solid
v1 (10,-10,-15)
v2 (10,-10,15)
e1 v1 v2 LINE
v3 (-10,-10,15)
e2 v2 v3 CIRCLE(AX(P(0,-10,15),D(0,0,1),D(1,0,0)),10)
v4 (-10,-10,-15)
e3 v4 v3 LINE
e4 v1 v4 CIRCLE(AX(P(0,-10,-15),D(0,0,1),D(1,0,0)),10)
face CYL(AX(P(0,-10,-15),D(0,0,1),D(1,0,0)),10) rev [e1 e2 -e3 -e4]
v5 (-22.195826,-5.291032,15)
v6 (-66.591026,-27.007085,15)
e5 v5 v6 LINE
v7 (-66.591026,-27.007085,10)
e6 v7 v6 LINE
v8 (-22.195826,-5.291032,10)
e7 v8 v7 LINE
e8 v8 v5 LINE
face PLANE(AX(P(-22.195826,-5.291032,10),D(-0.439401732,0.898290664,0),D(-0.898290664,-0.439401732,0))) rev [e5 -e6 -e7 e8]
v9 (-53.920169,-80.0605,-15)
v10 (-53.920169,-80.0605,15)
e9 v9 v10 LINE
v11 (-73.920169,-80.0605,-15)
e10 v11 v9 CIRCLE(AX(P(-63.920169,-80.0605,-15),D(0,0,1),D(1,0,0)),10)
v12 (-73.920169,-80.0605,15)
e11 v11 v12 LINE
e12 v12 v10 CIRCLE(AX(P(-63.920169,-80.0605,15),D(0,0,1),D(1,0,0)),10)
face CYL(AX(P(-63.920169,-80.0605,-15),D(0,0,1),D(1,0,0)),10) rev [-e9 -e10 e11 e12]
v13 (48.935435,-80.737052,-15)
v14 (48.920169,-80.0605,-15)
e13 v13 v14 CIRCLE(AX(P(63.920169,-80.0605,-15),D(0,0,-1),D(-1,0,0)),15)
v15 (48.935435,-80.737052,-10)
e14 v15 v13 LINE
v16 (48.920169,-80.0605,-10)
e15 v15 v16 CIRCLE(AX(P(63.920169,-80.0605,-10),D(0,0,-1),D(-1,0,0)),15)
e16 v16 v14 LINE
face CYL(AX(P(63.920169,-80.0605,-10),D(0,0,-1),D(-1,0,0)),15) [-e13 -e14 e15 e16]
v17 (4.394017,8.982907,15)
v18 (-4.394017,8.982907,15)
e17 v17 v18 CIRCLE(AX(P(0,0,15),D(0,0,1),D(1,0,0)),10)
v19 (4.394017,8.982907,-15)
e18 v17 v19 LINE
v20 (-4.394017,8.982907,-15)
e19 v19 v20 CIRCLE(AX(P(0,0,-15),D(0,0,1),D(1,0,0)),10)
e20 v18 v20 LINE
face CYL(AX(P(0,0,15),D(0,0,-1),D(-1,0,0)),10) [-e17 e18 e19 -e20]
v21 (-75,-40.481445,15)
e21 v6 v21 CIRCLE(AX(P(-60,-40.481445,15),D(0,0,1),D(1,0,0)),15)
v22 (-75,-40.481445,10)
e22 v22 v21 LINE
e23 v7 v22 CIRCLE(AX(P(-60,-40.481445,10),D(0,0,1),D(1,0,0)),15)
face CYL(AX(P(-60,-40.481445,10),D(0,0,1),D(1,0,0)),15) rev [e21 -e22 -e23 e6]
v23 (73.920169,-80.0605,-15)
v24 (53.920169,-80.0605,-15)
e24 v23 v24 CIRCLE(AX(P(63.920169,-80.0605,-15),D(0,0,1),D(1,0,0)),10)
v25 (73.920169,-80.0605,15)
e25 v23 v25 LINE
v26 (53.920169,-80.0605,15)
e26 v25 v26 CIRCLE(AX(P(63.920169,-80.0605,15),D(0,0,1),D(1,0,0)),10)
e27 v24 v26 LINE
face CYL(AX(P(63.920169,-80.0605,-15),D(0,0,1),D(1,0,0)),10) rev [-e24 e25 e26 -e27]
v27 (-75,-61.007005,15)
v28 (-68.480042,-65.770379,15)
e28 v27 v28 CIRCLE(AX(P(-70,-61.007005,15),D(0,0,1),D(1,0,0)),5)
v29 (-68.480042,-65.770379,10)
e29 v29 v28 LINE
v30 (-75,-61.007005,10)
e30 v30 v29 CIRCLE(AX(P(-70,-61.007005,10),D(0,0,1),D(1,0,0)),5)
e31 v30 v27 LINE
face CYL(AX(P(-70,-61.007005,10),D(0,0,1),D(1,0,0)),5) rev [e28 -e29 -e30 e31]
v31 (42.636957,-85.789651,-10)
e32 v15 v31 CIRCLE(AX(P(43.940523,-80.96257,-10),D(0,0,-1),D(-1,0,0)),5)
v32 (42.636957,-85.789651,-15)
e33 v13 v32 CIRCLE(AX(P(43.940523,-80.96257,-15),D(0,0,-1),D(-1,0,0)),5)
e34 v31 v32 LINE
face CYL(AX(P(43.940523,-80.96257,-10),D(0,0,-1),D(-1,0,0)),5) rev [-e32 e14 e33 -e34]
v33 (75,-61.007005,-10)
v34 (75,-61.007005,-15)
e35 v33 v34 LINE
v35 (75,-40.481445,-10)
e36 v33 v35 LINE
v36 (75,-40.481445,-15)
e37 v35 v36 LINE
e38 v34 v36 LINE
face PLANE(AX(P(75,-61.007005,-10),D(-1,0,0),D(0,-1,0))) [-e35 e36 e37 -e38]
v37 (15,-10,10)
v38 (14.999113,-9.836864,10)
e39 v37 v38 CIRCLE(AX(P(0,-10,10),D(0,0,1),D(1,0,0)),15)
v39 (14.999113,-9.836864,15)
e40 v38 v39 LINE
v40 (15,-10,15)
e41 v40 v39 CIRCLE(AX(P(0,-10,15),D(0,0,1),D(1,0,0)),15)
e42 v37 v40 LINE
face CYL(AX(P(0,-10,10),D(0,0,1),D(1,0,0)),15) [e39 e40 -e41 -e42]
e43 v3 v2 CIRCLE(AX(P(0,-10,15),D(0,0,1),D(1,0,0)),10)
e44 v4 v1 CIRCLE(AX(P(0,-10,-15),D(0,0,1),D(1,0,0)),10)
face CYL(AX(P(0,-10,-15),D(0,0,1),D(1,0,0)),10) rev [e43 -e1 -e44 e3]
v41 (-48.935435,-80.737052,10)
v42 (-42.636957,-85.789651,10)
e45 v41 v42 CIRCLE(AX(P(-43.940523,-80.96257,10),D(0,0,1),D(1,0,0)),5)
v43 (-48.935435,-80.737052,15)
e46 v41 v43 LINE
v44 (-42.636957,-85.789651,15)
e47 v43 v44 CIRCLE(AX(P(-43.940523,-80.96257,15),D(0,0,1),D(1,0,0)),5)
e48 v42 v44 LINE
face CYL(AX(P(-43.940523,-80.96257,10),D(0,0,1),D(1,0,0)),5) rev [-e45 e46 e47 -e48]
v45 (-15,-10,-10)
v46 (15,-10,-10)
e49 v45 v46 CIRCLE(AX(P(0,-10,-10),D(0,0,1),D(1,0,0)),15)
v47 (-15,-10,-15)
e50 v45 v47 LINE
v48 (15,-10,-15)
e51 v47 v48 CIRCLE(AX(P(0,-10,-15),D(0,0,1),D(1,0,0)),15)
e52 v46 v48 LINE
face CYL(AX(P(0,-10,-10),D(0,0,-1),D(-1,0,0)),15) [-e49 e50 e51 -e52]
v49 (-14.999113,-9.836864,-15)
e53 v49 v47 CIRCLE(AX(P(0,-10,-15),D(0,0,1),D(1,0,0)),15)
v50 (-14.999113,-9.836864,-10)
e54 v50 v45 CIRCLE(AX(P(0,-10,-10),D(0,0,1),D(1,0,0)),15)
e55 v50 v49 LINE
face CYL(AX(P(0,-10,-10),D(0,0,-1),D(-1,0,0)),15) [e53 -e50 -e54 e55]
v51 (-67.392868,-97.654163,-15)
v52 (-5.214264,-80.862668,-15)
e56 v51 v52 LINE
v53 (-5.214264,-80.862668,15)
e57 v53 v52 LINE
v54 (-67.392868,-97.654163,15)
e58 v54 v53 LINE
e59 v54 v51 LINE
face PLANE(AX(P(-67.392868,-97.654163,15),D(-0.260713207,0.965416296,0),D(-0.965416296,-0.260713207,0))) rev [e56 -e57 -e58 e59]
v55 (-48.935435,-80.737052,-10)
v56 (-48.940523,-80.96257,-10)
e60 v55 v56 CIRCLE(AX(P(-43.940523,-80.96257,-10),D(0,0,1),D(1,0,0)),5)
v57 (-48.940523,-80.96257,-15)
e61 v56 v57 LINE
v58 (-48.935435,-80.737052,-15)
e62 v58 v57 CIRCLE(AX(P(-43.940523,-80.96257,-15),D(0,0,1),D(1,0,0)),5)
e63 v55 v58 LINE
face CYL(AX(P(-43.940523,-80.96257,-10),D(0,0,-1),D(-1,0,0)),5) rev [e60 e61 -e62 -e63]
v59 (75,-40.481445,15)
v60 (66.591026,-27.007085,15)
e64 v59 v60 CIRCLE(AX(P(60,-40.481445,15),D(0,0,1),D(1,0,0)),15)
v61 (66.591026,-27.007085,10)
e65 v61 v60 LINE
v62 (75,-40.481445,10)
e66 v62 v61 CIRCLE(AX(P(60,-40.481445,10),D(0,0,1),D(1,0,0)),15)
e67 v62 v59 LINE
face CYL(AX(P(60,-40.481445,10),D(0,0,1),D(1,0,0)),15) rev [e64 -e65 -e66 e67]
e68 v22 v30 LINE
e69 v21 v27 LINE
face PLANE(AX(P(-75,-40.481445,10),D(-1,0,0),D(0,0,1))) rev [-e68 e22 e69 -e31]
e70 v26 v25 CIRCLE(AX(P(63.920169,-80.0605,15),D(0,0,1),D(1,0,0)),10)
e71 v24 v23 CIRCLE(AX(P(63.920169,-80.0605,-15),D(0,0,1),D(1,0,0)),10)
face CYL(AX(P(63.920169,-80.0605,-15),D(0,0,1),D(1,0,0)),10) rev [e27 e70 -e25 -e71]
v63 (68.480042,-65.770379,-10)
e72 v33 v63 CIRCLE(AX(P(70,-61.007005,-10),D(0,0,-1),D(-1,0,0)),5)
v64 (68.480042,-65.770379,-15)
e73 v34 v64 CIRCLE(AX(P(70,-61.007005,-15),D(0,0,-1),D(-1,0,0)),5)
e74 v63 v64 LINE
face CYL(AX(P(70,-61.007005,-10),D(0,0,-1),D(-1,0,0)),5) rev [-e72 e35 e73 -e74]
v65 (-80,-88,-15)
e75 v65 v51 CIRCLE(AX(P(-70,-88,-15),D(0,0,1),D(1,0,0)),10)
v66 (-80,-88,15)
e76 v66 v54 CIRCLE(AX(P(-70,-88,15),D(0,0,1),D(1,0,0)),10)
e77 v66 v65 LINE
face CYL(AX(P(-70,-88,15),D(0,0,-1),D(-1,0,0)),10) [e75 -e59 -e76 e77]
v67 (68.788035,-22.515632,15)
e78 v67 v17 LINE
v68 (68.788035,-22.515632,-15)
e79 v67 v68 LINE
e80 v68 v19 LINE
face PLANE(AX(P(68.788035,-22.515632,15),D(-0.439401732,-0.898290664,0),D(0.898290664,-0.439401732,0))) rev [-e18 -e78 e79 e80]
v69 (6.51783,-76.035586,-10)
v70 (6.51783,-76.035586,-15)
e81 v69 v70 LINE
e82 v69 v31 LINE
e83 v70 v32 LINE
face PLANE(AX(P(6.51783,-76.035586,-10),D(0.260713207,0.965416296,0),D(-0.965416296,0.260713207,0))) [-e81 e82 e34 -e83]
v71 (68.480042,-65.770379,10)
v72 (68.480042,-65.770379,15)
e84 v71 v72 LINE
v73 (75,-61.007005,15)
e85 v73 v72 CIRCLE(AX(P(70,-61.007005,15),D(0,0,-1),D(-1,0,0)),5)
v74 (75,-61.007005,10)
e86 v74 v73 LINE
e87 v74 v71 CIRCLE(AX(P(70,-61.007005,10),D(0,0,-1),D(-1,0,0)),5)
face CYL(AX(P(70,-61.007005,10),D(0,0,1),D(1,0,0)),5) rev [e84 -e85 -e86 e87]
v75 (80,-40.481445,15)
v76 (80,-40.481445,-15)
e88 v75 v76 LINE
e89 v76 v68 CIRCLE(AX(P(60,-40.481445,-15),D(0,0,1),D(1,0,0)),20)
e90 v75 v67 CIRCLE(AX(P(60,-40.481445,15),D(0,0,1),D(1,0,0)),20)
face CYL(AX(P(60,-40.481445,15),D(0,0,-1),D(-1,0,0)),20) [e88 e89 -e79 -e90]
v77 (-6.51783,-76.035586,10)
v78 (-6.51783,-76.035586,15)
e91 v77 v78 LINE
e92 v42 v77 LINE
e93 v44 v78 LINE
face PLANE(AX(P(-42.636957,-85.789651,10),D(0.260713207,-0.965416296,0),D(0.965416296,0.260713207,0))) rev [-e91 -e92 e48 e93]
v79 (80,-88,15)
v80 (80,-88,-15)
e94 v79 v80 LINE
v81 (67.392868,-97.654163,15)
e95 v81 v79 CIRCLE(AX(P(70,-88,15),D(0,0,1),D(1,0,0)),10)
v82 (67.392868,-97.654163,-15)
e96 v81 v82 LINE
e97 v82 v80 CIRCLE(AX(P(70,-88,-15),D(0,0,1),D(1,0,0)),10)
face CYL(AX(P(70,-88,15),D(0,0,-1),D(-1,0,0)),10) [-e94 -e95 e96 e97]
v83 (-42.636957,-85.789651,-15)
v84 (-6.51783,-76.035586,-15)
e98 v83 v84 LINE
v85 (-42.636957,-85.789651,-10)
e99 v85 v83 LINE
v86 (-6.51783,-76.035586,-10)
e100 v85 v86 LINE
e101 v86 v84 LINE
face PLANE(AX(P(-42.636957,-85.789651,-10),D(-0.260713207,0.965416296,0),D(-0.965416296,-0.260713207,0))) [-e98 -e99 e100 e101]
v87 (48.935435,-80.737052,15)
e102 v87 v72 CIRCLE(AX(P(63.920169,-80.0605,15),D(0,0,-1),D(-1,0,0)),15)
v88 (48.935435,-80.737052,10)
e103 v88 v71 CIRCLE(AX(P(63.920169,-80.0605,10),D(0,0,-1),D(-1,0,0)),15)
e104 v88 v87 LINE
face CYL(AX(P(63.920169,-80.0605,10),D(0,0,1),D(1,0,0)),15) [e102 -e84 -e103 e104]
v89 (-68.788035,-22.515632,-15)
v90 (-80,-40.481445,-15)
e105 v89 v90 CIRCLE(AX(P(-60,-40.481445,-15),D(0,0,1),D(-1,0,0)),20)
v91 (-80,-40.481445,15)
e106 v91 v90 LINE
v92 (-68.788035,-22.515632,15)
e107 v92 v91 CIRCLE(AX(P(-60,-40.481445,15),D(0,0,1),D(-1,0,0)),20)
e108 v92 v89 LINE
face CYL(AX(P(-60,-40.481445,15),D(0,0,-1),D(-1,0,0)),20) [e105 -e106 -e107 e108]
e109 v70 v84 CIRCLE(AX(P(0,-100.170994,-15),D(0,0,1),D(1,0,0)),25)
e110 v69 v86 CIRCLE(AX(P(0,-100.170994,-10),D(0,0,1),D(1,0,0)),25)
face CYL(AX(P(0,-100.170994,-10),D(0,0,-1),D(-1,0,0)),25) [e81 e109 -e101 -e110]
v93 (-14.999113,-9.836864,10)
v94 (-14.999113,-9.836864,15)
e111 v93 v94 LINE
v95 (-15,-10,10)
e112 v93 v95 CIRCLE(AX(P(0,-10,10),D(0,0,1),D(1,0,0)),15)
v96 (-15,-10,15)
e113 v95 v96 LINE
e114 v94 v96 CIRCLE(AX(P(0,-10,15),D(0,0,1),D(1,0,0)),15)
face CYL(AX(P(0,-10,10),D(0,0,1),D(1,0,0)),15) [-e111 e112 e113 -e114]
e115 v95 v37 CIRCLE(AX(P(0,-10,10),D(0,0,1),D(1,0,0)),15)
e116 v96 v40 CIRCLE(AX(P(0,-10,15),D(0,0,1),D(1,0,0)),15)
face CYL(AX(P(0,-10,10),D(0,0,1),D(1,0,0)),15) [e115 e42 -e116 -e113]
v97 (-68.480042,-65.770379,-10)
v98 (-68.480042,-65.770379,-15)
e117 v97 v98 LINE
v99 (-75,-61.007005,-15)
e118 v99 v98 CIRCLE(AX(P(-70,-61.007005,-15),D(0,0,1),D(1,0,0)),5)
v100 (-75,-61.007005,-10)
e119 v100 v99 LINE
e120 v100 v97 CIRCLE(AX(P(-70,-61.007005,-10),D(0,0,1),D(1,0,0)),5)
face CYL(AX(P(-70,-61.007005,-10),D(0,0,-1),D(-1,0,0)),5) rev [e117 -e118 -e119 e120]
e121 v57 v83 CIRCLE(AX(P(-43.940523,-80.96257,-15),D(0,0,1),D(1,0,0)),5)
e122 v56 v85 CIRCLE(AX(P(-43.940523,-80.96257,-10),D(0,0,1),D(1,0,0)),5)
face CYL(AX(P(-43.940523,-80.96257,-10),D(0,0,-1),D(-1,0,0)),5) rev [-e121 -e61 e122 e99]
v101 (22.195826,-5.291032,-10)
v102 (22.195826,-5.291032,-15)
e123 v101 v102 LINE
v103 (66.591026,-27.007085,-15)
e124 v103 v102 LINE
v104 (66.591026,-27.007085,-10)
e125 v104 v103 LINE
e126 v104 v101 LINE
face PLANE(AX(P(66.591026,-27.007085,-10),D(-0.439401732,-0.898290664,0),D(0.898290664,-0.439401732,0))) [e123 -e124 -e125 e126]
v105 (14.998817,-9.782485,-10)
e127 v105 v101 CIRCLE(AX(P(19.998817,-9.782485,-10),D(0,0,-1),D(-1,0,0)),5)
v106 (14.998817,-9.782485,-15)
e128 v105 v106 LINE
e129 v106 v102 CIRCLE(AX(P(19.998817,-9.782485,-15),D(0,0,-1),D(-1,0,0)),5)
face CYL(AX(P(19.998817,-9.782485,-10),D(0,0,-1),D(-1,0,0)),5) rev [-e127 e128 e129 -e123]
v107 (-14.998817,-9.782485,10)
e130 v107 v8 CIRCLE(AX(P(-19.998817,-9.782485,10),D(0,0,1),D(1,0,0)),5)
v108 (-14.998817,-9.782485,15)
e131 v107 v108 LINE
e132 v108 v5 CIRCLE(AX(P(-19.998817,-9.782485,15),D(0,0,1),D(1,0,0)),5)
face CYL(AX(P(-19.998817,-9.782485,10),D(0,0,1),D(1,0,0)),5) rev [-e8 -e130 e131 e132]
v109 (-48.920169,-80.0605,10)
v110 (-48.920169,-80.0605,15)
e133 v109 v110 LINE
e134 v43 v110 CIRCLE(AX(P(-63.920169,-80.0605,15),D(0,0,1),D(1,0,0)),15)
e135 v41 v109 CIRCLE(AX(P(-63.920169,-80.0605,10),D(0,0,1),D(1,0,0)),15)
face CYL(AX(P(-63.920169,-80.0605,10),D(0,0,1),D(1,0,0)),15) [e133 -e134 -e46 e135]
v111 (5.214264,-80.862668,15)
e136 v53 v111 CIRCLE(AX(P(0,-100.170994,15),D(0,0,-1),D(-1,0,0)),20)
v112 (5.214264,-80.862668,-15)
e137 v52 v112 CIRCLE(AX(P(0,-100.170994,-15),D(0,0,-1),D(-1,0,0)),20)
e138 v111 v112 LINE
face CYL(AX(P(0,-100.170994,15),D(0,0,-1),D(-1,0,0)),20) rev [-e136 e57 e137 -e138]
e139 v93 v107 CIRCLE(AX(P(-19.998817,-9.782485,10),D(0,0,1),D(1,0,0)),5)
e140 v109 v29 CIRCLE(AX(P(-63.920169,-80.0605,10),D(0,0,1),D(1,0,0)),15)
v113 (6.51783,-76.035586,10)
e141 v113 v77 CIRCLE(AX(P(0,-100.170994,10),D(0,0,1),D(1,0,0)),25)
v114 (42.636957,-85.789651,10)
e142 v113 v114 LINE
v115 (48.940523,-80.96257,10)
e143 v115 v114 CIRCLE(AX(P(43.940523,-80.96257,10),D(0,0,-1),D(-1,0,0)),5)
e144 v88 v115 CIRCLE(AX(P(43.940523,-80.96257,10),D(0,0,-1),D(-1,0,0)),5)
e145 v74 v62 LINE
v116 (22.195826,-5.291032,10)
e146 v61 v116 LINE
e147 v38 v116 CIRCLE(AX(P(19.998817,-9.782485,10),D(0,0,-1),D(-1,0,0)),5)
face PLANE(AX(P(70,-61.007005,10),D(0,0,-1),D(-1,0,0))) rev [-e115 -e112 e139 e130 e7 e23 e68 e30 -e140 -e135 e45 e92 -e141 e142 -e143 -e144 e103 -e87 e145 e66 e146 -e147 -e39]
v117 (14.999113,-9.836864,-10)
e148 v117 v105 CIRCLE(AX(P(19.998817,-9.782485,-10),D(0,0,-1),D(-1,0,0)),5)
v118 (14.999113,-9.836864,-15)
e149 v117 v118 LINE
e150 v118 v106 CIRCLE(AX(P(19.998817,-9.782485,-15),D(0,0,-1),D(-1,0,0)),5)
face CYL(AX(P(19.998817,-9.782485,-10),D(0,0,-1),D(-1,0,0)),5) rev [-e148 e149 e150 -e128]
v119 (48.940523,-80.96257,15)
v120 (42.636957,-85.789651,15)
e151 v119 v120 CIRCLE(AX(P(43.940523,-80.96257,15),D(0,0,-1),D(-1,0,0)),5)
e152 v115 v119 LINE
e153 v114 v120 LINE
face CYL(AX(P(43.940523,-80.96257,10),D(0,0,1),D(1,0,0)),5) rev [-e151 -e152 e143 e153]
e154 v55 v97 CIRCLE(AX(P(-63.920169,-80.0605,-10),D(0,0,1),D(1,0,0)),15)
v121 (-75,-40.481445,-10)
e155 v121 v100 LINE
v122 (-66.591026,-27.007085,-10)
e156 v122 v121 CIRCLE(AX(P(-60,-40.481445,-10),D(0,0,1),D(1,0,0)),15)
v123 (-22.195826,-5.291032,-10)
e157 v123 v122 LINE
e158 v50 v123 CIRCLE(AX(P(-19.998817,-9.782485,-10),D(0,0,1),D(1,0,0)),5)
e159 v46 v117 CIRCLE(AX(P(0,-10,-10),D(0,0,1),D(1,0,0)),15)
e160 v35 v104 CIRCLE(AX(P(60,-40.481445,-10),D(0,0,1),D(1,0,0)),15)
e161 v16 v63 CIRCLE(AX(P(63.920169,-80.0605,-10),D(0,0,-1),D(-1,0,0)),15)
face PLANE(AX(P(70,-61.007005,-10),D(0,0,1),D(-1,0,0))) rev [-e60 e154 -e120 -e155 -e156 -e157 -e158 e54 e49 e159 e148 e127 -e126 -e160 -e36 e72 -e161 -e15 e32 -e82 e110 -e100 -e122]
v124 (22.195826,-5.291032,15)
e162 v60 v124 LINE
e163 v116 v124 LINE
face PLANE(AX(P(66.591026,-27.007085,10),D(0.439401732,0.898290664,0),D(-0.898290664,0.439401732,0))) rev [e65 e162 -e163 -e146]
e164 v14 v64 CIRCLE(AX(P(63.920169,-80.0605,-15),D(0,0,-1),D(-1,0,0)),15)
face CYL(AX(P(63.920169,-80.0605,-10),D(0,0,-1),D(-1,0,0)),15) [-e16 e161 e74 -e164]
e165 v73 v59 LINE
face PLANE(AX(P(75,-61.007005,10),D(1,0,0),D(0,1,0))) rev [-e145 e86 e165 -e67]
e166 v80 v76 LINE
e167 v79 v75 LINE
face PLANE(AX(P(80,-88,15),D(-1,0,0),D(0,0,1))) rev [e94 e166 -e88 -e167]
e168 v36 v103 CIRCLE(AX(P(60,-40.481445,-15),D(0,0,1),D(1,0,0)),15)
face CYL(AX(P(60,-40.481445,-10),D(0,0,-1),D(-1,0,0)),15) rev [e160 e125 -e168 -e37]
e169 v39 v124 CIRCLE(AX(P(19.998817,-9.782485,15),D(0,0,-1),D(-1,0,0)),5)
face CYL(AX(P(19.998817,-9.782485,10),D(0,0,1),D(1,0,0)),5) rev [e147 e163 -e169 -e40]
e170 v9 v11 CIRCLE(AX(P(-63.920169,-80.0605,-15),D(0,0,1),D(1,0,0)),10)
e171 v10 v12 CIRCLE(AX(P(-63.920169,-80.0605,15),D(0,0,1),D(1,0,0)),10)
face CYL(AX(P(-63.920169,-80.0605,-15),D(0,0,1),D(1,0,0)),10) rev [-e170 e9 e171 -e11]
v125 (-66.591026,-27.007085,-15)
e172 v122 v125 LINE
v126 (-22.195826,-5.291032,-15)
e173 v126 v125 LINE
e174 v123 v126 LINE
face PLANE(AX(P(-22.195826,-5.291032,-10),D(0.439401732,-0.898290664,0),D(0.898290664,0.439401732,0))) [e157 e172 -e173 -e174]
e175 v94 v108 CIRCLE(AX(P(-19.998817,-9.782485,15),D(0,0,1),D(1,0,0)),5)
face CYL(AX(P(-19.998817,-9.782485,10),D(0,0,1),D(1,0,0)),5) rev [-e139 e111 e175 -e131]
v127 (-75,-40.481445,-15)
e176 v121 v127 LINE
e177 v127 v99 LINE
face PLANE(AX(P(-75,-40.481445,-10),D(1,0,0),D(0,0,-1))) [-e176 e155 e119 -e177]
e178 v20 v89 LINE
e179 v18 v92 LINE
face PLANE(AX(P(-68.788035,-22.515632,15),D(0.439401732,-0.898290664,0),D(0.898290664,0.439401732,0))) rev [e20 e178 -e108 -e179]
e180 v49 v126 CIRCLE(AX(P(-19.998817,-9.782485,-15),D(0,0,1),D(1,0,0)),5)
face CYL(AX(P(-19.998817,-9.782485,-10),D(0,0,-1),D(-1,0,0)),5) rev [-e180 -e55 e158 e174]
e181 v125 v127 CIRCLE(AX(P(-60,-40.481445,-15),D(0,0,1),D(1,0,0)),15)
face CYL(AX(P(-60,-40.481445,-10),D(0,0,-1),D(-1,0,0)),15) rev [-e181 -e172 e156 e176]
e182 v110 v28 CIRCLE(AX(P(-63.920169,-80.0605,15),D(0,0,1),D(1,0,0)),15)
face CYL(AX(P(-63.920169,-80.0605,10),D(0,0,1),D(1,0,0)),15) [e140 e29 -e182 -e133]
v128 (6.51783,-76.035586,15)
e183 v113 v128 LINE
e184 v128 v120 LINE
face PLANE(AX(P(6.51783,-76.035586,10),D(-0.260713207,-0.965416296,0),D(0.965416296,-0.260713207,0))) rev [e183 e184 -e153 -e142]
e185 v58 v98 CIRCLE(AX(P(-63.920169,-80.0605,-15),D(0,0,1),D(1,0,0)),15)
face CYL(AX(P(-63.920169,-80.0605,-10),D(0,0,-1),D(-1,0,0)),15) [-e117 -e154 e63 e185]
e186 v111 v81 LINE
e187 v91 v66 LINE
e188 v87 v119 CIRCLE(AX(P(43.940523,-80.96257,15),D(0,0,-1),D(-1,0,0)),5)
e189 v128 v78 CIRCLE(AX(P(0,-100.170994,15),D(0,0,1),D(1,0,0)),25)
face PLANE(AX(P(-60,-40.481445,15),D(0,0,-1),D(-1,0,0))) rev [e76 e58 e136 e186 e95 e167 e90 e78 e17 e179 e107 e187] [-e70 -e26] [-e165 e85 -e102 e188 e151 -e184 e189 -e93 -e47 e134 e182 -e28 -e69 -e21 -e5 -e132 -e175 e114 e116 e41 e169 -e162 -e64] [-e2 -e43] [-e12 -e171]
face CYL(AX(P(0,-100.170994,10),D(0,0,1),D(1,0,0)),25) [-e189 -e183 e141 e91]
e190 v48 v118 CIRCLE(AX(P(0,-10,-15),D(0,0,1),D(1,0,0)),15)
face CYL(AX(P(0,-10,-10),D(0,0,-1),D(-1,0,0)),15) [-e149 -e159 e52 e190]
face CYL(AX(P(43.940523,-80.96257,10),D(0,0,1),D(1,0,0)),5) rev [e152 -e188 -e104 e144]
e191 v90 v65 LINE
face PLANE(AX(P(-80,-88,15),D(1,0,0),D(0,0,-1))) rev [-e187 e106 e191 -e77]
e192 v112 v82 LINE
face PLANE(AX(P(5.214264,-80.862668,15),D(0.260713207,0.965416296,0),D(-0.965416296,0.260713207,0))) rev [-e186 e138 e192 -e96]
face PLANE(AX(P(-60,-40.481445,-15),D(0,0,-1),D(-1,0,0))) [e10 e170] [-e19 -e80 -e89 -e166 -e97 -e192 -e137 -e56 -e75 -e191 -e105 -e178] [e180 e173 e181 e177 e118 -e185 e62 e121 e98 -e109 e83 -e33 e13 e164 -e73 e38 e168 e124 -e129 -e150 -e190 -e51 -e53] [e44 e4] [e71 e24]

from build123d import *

# Parameters (mm, degrees)
BRACKET_PLATE_DEPTH          = 15
FRONT_FACE_POCKET_DEPTH      = 5
MOUNTING_HOLES_X3_DEPTH      = 129.953479984
MOUNTING_HOLES_X3_DEPTH_BACK = 129.953479984
MOUNTING_HOLES_SKETCH_R      = 10


with BuildPart() as part:
    # Bracket Outline Sketch → Bracket Plate (new, symmetric)
    with BuildSketch(Plane.XY):
        with BuildLine():
            Line((-80, -88), (-80, -40.481444811))
            ThreePointArc((-80, -40.481444811), (-76.967037057, -29.892787979), (-68.78803465, -22.515631526))
            Line((-68.78803465, -22.515631526), (-4.394017325, 8.982906643))
            ThreePointArc((-4.394017325, 8.982906643), (0, 10), (4.394017325, 8.982906643))
            Line((4.394017325, 8.982906643), (68.78803465, -22.515631526))
            ThreePointArc((68.78803465, -22.515631526), (76.967037057, -29.892787979), (80, -40.481444811))
            Line((80, -40.481444811), (80, -88))
            ThreePointArc((80, -88), (76.079830561, -95.939500006), (67.39286793, -97.654162955))
            Line((67.39286793, -97.654162955), (5.21426414, -80.862667644))
            ThreePointArc((5.21426414, -80.862667644), (0, -80.170993555), (-5.21426414, -80.862667644))
            Line((-5.21426414, -80.862667644), (-67.39286793, -97.654162955))
            ThreePointArc((-67.39286793, -97.654162955), (-76.079830561, -95.939500006), (-80, -88))
        make_face()
    extrude(amount=BRACKET_PLATE_DEPTH, both=True)

    # Face Pocket Sketch → Front Face Pocket (cut)
    with BuildSketch(Plane.XY.offset(15)):
        with BuildLine():
            Line((75, -61.007005292), (75, -40.481444811))
            ThreePointArc((75, -40.481444811), (72.725277793, -32.539952187), (66.591025987, -27.007084847))
            Line((66.591025987, -27.007084847), (22.195825808, -5.291031626))
            ThreePointArc((22.195825808, -5.291031626), (17.328625574, -5.555183565), (14.999112859, -9.83686371))
            ThreePointArc((14.999112859, -9.83686371), (0, -25), (-14.999112859, -9.83686371))
            ThreePointArc((-14.999112859, -9.83686371), (-17.328625574, -5.555183565), (-22.195825808, -5.291031626))
            Line((-22.195825808, -5.291031626), (-66.591025987, -27.007084847))
            ThreePointArc((-66.591025987, -27.007084847), (-72.725277793, -32.539952187), (-75, -40.481444811))
            Line((-75, -40.481444811), (-75, -61.007005292))
            ThreePointArc((-75, -61.007005292), (-72.949594192, -65.044318025), (-68.48004236, -65.770378967))
            ThreePointArc((-68.48004236, -65.770378967), (-54.800423598, -68.151249984), (-48.935434642, -80.737052336))
            ThreePointArc((-48.935434642, -80.737052336), (-47.069212384, -84.862736832), (-42.636957008, -85.789651261))
            Line((-42.636957008, -85.789651261), (-6.517830175, -76.035586166))
            ThreePointArc((-6.517830175, -76.035586166), (0, -75.170993555), (6.517830175, -76.035586166))
            Line((6.517830175, -76.035586166), (42.636957008, -85.789651261))
            ThreePointArc((42.636957008, -85.789651261), (47.069212384, -84.862736832), (48.935434642, -80.737052336))
            ThreePointArc((48.935434642, -80.737052336), (54.800423598, -68.151249984), (68.48004236, -65.770378967))
            ThreePointArc((68.48004236, -65.770378967), (72.949594192, -65.044318025), (75, -61.007005292))
        make_face()
    front_face_pocket = extrude(amount=-FRONT_FACE_POCKET_DEPTH, mode=Mode.SUBTRACT)

    # Back Face Pocket Mirror: Front Face Pocket across plane
    add(front_face_pocket.mirror(Plane.XY), mode=Mode.SUBTRACT)

    # Mounting Holes Sketch → Mounting Holes x3 (cut, two sides: drawn at the far end of the back side and taken through both)
    with BuildSketch(Plane.XY.offset(10).offset(-MOUNTING_HOLES_X3_DEPTH_BACK)):
        with Locations((-63.920169439, -80.060499994)):
            Circle(MOUNTING_HOLES_SKETCH_R)
        with Locations((0, -10)):
            Circle(MOUNTING_HOLES_SKETCH_R)
        with Locations((63.920169439, -80.060499994)):
            Circle(MOUNTING_HOLES_SKETCH_R)
    extrude(amount=MOUNTING_HOLES_X3_DEPTH + MOUNTING_HOLES_X3_DEPTH_BACK, mode=Mode.SUBTRACT)


solid = part.part
